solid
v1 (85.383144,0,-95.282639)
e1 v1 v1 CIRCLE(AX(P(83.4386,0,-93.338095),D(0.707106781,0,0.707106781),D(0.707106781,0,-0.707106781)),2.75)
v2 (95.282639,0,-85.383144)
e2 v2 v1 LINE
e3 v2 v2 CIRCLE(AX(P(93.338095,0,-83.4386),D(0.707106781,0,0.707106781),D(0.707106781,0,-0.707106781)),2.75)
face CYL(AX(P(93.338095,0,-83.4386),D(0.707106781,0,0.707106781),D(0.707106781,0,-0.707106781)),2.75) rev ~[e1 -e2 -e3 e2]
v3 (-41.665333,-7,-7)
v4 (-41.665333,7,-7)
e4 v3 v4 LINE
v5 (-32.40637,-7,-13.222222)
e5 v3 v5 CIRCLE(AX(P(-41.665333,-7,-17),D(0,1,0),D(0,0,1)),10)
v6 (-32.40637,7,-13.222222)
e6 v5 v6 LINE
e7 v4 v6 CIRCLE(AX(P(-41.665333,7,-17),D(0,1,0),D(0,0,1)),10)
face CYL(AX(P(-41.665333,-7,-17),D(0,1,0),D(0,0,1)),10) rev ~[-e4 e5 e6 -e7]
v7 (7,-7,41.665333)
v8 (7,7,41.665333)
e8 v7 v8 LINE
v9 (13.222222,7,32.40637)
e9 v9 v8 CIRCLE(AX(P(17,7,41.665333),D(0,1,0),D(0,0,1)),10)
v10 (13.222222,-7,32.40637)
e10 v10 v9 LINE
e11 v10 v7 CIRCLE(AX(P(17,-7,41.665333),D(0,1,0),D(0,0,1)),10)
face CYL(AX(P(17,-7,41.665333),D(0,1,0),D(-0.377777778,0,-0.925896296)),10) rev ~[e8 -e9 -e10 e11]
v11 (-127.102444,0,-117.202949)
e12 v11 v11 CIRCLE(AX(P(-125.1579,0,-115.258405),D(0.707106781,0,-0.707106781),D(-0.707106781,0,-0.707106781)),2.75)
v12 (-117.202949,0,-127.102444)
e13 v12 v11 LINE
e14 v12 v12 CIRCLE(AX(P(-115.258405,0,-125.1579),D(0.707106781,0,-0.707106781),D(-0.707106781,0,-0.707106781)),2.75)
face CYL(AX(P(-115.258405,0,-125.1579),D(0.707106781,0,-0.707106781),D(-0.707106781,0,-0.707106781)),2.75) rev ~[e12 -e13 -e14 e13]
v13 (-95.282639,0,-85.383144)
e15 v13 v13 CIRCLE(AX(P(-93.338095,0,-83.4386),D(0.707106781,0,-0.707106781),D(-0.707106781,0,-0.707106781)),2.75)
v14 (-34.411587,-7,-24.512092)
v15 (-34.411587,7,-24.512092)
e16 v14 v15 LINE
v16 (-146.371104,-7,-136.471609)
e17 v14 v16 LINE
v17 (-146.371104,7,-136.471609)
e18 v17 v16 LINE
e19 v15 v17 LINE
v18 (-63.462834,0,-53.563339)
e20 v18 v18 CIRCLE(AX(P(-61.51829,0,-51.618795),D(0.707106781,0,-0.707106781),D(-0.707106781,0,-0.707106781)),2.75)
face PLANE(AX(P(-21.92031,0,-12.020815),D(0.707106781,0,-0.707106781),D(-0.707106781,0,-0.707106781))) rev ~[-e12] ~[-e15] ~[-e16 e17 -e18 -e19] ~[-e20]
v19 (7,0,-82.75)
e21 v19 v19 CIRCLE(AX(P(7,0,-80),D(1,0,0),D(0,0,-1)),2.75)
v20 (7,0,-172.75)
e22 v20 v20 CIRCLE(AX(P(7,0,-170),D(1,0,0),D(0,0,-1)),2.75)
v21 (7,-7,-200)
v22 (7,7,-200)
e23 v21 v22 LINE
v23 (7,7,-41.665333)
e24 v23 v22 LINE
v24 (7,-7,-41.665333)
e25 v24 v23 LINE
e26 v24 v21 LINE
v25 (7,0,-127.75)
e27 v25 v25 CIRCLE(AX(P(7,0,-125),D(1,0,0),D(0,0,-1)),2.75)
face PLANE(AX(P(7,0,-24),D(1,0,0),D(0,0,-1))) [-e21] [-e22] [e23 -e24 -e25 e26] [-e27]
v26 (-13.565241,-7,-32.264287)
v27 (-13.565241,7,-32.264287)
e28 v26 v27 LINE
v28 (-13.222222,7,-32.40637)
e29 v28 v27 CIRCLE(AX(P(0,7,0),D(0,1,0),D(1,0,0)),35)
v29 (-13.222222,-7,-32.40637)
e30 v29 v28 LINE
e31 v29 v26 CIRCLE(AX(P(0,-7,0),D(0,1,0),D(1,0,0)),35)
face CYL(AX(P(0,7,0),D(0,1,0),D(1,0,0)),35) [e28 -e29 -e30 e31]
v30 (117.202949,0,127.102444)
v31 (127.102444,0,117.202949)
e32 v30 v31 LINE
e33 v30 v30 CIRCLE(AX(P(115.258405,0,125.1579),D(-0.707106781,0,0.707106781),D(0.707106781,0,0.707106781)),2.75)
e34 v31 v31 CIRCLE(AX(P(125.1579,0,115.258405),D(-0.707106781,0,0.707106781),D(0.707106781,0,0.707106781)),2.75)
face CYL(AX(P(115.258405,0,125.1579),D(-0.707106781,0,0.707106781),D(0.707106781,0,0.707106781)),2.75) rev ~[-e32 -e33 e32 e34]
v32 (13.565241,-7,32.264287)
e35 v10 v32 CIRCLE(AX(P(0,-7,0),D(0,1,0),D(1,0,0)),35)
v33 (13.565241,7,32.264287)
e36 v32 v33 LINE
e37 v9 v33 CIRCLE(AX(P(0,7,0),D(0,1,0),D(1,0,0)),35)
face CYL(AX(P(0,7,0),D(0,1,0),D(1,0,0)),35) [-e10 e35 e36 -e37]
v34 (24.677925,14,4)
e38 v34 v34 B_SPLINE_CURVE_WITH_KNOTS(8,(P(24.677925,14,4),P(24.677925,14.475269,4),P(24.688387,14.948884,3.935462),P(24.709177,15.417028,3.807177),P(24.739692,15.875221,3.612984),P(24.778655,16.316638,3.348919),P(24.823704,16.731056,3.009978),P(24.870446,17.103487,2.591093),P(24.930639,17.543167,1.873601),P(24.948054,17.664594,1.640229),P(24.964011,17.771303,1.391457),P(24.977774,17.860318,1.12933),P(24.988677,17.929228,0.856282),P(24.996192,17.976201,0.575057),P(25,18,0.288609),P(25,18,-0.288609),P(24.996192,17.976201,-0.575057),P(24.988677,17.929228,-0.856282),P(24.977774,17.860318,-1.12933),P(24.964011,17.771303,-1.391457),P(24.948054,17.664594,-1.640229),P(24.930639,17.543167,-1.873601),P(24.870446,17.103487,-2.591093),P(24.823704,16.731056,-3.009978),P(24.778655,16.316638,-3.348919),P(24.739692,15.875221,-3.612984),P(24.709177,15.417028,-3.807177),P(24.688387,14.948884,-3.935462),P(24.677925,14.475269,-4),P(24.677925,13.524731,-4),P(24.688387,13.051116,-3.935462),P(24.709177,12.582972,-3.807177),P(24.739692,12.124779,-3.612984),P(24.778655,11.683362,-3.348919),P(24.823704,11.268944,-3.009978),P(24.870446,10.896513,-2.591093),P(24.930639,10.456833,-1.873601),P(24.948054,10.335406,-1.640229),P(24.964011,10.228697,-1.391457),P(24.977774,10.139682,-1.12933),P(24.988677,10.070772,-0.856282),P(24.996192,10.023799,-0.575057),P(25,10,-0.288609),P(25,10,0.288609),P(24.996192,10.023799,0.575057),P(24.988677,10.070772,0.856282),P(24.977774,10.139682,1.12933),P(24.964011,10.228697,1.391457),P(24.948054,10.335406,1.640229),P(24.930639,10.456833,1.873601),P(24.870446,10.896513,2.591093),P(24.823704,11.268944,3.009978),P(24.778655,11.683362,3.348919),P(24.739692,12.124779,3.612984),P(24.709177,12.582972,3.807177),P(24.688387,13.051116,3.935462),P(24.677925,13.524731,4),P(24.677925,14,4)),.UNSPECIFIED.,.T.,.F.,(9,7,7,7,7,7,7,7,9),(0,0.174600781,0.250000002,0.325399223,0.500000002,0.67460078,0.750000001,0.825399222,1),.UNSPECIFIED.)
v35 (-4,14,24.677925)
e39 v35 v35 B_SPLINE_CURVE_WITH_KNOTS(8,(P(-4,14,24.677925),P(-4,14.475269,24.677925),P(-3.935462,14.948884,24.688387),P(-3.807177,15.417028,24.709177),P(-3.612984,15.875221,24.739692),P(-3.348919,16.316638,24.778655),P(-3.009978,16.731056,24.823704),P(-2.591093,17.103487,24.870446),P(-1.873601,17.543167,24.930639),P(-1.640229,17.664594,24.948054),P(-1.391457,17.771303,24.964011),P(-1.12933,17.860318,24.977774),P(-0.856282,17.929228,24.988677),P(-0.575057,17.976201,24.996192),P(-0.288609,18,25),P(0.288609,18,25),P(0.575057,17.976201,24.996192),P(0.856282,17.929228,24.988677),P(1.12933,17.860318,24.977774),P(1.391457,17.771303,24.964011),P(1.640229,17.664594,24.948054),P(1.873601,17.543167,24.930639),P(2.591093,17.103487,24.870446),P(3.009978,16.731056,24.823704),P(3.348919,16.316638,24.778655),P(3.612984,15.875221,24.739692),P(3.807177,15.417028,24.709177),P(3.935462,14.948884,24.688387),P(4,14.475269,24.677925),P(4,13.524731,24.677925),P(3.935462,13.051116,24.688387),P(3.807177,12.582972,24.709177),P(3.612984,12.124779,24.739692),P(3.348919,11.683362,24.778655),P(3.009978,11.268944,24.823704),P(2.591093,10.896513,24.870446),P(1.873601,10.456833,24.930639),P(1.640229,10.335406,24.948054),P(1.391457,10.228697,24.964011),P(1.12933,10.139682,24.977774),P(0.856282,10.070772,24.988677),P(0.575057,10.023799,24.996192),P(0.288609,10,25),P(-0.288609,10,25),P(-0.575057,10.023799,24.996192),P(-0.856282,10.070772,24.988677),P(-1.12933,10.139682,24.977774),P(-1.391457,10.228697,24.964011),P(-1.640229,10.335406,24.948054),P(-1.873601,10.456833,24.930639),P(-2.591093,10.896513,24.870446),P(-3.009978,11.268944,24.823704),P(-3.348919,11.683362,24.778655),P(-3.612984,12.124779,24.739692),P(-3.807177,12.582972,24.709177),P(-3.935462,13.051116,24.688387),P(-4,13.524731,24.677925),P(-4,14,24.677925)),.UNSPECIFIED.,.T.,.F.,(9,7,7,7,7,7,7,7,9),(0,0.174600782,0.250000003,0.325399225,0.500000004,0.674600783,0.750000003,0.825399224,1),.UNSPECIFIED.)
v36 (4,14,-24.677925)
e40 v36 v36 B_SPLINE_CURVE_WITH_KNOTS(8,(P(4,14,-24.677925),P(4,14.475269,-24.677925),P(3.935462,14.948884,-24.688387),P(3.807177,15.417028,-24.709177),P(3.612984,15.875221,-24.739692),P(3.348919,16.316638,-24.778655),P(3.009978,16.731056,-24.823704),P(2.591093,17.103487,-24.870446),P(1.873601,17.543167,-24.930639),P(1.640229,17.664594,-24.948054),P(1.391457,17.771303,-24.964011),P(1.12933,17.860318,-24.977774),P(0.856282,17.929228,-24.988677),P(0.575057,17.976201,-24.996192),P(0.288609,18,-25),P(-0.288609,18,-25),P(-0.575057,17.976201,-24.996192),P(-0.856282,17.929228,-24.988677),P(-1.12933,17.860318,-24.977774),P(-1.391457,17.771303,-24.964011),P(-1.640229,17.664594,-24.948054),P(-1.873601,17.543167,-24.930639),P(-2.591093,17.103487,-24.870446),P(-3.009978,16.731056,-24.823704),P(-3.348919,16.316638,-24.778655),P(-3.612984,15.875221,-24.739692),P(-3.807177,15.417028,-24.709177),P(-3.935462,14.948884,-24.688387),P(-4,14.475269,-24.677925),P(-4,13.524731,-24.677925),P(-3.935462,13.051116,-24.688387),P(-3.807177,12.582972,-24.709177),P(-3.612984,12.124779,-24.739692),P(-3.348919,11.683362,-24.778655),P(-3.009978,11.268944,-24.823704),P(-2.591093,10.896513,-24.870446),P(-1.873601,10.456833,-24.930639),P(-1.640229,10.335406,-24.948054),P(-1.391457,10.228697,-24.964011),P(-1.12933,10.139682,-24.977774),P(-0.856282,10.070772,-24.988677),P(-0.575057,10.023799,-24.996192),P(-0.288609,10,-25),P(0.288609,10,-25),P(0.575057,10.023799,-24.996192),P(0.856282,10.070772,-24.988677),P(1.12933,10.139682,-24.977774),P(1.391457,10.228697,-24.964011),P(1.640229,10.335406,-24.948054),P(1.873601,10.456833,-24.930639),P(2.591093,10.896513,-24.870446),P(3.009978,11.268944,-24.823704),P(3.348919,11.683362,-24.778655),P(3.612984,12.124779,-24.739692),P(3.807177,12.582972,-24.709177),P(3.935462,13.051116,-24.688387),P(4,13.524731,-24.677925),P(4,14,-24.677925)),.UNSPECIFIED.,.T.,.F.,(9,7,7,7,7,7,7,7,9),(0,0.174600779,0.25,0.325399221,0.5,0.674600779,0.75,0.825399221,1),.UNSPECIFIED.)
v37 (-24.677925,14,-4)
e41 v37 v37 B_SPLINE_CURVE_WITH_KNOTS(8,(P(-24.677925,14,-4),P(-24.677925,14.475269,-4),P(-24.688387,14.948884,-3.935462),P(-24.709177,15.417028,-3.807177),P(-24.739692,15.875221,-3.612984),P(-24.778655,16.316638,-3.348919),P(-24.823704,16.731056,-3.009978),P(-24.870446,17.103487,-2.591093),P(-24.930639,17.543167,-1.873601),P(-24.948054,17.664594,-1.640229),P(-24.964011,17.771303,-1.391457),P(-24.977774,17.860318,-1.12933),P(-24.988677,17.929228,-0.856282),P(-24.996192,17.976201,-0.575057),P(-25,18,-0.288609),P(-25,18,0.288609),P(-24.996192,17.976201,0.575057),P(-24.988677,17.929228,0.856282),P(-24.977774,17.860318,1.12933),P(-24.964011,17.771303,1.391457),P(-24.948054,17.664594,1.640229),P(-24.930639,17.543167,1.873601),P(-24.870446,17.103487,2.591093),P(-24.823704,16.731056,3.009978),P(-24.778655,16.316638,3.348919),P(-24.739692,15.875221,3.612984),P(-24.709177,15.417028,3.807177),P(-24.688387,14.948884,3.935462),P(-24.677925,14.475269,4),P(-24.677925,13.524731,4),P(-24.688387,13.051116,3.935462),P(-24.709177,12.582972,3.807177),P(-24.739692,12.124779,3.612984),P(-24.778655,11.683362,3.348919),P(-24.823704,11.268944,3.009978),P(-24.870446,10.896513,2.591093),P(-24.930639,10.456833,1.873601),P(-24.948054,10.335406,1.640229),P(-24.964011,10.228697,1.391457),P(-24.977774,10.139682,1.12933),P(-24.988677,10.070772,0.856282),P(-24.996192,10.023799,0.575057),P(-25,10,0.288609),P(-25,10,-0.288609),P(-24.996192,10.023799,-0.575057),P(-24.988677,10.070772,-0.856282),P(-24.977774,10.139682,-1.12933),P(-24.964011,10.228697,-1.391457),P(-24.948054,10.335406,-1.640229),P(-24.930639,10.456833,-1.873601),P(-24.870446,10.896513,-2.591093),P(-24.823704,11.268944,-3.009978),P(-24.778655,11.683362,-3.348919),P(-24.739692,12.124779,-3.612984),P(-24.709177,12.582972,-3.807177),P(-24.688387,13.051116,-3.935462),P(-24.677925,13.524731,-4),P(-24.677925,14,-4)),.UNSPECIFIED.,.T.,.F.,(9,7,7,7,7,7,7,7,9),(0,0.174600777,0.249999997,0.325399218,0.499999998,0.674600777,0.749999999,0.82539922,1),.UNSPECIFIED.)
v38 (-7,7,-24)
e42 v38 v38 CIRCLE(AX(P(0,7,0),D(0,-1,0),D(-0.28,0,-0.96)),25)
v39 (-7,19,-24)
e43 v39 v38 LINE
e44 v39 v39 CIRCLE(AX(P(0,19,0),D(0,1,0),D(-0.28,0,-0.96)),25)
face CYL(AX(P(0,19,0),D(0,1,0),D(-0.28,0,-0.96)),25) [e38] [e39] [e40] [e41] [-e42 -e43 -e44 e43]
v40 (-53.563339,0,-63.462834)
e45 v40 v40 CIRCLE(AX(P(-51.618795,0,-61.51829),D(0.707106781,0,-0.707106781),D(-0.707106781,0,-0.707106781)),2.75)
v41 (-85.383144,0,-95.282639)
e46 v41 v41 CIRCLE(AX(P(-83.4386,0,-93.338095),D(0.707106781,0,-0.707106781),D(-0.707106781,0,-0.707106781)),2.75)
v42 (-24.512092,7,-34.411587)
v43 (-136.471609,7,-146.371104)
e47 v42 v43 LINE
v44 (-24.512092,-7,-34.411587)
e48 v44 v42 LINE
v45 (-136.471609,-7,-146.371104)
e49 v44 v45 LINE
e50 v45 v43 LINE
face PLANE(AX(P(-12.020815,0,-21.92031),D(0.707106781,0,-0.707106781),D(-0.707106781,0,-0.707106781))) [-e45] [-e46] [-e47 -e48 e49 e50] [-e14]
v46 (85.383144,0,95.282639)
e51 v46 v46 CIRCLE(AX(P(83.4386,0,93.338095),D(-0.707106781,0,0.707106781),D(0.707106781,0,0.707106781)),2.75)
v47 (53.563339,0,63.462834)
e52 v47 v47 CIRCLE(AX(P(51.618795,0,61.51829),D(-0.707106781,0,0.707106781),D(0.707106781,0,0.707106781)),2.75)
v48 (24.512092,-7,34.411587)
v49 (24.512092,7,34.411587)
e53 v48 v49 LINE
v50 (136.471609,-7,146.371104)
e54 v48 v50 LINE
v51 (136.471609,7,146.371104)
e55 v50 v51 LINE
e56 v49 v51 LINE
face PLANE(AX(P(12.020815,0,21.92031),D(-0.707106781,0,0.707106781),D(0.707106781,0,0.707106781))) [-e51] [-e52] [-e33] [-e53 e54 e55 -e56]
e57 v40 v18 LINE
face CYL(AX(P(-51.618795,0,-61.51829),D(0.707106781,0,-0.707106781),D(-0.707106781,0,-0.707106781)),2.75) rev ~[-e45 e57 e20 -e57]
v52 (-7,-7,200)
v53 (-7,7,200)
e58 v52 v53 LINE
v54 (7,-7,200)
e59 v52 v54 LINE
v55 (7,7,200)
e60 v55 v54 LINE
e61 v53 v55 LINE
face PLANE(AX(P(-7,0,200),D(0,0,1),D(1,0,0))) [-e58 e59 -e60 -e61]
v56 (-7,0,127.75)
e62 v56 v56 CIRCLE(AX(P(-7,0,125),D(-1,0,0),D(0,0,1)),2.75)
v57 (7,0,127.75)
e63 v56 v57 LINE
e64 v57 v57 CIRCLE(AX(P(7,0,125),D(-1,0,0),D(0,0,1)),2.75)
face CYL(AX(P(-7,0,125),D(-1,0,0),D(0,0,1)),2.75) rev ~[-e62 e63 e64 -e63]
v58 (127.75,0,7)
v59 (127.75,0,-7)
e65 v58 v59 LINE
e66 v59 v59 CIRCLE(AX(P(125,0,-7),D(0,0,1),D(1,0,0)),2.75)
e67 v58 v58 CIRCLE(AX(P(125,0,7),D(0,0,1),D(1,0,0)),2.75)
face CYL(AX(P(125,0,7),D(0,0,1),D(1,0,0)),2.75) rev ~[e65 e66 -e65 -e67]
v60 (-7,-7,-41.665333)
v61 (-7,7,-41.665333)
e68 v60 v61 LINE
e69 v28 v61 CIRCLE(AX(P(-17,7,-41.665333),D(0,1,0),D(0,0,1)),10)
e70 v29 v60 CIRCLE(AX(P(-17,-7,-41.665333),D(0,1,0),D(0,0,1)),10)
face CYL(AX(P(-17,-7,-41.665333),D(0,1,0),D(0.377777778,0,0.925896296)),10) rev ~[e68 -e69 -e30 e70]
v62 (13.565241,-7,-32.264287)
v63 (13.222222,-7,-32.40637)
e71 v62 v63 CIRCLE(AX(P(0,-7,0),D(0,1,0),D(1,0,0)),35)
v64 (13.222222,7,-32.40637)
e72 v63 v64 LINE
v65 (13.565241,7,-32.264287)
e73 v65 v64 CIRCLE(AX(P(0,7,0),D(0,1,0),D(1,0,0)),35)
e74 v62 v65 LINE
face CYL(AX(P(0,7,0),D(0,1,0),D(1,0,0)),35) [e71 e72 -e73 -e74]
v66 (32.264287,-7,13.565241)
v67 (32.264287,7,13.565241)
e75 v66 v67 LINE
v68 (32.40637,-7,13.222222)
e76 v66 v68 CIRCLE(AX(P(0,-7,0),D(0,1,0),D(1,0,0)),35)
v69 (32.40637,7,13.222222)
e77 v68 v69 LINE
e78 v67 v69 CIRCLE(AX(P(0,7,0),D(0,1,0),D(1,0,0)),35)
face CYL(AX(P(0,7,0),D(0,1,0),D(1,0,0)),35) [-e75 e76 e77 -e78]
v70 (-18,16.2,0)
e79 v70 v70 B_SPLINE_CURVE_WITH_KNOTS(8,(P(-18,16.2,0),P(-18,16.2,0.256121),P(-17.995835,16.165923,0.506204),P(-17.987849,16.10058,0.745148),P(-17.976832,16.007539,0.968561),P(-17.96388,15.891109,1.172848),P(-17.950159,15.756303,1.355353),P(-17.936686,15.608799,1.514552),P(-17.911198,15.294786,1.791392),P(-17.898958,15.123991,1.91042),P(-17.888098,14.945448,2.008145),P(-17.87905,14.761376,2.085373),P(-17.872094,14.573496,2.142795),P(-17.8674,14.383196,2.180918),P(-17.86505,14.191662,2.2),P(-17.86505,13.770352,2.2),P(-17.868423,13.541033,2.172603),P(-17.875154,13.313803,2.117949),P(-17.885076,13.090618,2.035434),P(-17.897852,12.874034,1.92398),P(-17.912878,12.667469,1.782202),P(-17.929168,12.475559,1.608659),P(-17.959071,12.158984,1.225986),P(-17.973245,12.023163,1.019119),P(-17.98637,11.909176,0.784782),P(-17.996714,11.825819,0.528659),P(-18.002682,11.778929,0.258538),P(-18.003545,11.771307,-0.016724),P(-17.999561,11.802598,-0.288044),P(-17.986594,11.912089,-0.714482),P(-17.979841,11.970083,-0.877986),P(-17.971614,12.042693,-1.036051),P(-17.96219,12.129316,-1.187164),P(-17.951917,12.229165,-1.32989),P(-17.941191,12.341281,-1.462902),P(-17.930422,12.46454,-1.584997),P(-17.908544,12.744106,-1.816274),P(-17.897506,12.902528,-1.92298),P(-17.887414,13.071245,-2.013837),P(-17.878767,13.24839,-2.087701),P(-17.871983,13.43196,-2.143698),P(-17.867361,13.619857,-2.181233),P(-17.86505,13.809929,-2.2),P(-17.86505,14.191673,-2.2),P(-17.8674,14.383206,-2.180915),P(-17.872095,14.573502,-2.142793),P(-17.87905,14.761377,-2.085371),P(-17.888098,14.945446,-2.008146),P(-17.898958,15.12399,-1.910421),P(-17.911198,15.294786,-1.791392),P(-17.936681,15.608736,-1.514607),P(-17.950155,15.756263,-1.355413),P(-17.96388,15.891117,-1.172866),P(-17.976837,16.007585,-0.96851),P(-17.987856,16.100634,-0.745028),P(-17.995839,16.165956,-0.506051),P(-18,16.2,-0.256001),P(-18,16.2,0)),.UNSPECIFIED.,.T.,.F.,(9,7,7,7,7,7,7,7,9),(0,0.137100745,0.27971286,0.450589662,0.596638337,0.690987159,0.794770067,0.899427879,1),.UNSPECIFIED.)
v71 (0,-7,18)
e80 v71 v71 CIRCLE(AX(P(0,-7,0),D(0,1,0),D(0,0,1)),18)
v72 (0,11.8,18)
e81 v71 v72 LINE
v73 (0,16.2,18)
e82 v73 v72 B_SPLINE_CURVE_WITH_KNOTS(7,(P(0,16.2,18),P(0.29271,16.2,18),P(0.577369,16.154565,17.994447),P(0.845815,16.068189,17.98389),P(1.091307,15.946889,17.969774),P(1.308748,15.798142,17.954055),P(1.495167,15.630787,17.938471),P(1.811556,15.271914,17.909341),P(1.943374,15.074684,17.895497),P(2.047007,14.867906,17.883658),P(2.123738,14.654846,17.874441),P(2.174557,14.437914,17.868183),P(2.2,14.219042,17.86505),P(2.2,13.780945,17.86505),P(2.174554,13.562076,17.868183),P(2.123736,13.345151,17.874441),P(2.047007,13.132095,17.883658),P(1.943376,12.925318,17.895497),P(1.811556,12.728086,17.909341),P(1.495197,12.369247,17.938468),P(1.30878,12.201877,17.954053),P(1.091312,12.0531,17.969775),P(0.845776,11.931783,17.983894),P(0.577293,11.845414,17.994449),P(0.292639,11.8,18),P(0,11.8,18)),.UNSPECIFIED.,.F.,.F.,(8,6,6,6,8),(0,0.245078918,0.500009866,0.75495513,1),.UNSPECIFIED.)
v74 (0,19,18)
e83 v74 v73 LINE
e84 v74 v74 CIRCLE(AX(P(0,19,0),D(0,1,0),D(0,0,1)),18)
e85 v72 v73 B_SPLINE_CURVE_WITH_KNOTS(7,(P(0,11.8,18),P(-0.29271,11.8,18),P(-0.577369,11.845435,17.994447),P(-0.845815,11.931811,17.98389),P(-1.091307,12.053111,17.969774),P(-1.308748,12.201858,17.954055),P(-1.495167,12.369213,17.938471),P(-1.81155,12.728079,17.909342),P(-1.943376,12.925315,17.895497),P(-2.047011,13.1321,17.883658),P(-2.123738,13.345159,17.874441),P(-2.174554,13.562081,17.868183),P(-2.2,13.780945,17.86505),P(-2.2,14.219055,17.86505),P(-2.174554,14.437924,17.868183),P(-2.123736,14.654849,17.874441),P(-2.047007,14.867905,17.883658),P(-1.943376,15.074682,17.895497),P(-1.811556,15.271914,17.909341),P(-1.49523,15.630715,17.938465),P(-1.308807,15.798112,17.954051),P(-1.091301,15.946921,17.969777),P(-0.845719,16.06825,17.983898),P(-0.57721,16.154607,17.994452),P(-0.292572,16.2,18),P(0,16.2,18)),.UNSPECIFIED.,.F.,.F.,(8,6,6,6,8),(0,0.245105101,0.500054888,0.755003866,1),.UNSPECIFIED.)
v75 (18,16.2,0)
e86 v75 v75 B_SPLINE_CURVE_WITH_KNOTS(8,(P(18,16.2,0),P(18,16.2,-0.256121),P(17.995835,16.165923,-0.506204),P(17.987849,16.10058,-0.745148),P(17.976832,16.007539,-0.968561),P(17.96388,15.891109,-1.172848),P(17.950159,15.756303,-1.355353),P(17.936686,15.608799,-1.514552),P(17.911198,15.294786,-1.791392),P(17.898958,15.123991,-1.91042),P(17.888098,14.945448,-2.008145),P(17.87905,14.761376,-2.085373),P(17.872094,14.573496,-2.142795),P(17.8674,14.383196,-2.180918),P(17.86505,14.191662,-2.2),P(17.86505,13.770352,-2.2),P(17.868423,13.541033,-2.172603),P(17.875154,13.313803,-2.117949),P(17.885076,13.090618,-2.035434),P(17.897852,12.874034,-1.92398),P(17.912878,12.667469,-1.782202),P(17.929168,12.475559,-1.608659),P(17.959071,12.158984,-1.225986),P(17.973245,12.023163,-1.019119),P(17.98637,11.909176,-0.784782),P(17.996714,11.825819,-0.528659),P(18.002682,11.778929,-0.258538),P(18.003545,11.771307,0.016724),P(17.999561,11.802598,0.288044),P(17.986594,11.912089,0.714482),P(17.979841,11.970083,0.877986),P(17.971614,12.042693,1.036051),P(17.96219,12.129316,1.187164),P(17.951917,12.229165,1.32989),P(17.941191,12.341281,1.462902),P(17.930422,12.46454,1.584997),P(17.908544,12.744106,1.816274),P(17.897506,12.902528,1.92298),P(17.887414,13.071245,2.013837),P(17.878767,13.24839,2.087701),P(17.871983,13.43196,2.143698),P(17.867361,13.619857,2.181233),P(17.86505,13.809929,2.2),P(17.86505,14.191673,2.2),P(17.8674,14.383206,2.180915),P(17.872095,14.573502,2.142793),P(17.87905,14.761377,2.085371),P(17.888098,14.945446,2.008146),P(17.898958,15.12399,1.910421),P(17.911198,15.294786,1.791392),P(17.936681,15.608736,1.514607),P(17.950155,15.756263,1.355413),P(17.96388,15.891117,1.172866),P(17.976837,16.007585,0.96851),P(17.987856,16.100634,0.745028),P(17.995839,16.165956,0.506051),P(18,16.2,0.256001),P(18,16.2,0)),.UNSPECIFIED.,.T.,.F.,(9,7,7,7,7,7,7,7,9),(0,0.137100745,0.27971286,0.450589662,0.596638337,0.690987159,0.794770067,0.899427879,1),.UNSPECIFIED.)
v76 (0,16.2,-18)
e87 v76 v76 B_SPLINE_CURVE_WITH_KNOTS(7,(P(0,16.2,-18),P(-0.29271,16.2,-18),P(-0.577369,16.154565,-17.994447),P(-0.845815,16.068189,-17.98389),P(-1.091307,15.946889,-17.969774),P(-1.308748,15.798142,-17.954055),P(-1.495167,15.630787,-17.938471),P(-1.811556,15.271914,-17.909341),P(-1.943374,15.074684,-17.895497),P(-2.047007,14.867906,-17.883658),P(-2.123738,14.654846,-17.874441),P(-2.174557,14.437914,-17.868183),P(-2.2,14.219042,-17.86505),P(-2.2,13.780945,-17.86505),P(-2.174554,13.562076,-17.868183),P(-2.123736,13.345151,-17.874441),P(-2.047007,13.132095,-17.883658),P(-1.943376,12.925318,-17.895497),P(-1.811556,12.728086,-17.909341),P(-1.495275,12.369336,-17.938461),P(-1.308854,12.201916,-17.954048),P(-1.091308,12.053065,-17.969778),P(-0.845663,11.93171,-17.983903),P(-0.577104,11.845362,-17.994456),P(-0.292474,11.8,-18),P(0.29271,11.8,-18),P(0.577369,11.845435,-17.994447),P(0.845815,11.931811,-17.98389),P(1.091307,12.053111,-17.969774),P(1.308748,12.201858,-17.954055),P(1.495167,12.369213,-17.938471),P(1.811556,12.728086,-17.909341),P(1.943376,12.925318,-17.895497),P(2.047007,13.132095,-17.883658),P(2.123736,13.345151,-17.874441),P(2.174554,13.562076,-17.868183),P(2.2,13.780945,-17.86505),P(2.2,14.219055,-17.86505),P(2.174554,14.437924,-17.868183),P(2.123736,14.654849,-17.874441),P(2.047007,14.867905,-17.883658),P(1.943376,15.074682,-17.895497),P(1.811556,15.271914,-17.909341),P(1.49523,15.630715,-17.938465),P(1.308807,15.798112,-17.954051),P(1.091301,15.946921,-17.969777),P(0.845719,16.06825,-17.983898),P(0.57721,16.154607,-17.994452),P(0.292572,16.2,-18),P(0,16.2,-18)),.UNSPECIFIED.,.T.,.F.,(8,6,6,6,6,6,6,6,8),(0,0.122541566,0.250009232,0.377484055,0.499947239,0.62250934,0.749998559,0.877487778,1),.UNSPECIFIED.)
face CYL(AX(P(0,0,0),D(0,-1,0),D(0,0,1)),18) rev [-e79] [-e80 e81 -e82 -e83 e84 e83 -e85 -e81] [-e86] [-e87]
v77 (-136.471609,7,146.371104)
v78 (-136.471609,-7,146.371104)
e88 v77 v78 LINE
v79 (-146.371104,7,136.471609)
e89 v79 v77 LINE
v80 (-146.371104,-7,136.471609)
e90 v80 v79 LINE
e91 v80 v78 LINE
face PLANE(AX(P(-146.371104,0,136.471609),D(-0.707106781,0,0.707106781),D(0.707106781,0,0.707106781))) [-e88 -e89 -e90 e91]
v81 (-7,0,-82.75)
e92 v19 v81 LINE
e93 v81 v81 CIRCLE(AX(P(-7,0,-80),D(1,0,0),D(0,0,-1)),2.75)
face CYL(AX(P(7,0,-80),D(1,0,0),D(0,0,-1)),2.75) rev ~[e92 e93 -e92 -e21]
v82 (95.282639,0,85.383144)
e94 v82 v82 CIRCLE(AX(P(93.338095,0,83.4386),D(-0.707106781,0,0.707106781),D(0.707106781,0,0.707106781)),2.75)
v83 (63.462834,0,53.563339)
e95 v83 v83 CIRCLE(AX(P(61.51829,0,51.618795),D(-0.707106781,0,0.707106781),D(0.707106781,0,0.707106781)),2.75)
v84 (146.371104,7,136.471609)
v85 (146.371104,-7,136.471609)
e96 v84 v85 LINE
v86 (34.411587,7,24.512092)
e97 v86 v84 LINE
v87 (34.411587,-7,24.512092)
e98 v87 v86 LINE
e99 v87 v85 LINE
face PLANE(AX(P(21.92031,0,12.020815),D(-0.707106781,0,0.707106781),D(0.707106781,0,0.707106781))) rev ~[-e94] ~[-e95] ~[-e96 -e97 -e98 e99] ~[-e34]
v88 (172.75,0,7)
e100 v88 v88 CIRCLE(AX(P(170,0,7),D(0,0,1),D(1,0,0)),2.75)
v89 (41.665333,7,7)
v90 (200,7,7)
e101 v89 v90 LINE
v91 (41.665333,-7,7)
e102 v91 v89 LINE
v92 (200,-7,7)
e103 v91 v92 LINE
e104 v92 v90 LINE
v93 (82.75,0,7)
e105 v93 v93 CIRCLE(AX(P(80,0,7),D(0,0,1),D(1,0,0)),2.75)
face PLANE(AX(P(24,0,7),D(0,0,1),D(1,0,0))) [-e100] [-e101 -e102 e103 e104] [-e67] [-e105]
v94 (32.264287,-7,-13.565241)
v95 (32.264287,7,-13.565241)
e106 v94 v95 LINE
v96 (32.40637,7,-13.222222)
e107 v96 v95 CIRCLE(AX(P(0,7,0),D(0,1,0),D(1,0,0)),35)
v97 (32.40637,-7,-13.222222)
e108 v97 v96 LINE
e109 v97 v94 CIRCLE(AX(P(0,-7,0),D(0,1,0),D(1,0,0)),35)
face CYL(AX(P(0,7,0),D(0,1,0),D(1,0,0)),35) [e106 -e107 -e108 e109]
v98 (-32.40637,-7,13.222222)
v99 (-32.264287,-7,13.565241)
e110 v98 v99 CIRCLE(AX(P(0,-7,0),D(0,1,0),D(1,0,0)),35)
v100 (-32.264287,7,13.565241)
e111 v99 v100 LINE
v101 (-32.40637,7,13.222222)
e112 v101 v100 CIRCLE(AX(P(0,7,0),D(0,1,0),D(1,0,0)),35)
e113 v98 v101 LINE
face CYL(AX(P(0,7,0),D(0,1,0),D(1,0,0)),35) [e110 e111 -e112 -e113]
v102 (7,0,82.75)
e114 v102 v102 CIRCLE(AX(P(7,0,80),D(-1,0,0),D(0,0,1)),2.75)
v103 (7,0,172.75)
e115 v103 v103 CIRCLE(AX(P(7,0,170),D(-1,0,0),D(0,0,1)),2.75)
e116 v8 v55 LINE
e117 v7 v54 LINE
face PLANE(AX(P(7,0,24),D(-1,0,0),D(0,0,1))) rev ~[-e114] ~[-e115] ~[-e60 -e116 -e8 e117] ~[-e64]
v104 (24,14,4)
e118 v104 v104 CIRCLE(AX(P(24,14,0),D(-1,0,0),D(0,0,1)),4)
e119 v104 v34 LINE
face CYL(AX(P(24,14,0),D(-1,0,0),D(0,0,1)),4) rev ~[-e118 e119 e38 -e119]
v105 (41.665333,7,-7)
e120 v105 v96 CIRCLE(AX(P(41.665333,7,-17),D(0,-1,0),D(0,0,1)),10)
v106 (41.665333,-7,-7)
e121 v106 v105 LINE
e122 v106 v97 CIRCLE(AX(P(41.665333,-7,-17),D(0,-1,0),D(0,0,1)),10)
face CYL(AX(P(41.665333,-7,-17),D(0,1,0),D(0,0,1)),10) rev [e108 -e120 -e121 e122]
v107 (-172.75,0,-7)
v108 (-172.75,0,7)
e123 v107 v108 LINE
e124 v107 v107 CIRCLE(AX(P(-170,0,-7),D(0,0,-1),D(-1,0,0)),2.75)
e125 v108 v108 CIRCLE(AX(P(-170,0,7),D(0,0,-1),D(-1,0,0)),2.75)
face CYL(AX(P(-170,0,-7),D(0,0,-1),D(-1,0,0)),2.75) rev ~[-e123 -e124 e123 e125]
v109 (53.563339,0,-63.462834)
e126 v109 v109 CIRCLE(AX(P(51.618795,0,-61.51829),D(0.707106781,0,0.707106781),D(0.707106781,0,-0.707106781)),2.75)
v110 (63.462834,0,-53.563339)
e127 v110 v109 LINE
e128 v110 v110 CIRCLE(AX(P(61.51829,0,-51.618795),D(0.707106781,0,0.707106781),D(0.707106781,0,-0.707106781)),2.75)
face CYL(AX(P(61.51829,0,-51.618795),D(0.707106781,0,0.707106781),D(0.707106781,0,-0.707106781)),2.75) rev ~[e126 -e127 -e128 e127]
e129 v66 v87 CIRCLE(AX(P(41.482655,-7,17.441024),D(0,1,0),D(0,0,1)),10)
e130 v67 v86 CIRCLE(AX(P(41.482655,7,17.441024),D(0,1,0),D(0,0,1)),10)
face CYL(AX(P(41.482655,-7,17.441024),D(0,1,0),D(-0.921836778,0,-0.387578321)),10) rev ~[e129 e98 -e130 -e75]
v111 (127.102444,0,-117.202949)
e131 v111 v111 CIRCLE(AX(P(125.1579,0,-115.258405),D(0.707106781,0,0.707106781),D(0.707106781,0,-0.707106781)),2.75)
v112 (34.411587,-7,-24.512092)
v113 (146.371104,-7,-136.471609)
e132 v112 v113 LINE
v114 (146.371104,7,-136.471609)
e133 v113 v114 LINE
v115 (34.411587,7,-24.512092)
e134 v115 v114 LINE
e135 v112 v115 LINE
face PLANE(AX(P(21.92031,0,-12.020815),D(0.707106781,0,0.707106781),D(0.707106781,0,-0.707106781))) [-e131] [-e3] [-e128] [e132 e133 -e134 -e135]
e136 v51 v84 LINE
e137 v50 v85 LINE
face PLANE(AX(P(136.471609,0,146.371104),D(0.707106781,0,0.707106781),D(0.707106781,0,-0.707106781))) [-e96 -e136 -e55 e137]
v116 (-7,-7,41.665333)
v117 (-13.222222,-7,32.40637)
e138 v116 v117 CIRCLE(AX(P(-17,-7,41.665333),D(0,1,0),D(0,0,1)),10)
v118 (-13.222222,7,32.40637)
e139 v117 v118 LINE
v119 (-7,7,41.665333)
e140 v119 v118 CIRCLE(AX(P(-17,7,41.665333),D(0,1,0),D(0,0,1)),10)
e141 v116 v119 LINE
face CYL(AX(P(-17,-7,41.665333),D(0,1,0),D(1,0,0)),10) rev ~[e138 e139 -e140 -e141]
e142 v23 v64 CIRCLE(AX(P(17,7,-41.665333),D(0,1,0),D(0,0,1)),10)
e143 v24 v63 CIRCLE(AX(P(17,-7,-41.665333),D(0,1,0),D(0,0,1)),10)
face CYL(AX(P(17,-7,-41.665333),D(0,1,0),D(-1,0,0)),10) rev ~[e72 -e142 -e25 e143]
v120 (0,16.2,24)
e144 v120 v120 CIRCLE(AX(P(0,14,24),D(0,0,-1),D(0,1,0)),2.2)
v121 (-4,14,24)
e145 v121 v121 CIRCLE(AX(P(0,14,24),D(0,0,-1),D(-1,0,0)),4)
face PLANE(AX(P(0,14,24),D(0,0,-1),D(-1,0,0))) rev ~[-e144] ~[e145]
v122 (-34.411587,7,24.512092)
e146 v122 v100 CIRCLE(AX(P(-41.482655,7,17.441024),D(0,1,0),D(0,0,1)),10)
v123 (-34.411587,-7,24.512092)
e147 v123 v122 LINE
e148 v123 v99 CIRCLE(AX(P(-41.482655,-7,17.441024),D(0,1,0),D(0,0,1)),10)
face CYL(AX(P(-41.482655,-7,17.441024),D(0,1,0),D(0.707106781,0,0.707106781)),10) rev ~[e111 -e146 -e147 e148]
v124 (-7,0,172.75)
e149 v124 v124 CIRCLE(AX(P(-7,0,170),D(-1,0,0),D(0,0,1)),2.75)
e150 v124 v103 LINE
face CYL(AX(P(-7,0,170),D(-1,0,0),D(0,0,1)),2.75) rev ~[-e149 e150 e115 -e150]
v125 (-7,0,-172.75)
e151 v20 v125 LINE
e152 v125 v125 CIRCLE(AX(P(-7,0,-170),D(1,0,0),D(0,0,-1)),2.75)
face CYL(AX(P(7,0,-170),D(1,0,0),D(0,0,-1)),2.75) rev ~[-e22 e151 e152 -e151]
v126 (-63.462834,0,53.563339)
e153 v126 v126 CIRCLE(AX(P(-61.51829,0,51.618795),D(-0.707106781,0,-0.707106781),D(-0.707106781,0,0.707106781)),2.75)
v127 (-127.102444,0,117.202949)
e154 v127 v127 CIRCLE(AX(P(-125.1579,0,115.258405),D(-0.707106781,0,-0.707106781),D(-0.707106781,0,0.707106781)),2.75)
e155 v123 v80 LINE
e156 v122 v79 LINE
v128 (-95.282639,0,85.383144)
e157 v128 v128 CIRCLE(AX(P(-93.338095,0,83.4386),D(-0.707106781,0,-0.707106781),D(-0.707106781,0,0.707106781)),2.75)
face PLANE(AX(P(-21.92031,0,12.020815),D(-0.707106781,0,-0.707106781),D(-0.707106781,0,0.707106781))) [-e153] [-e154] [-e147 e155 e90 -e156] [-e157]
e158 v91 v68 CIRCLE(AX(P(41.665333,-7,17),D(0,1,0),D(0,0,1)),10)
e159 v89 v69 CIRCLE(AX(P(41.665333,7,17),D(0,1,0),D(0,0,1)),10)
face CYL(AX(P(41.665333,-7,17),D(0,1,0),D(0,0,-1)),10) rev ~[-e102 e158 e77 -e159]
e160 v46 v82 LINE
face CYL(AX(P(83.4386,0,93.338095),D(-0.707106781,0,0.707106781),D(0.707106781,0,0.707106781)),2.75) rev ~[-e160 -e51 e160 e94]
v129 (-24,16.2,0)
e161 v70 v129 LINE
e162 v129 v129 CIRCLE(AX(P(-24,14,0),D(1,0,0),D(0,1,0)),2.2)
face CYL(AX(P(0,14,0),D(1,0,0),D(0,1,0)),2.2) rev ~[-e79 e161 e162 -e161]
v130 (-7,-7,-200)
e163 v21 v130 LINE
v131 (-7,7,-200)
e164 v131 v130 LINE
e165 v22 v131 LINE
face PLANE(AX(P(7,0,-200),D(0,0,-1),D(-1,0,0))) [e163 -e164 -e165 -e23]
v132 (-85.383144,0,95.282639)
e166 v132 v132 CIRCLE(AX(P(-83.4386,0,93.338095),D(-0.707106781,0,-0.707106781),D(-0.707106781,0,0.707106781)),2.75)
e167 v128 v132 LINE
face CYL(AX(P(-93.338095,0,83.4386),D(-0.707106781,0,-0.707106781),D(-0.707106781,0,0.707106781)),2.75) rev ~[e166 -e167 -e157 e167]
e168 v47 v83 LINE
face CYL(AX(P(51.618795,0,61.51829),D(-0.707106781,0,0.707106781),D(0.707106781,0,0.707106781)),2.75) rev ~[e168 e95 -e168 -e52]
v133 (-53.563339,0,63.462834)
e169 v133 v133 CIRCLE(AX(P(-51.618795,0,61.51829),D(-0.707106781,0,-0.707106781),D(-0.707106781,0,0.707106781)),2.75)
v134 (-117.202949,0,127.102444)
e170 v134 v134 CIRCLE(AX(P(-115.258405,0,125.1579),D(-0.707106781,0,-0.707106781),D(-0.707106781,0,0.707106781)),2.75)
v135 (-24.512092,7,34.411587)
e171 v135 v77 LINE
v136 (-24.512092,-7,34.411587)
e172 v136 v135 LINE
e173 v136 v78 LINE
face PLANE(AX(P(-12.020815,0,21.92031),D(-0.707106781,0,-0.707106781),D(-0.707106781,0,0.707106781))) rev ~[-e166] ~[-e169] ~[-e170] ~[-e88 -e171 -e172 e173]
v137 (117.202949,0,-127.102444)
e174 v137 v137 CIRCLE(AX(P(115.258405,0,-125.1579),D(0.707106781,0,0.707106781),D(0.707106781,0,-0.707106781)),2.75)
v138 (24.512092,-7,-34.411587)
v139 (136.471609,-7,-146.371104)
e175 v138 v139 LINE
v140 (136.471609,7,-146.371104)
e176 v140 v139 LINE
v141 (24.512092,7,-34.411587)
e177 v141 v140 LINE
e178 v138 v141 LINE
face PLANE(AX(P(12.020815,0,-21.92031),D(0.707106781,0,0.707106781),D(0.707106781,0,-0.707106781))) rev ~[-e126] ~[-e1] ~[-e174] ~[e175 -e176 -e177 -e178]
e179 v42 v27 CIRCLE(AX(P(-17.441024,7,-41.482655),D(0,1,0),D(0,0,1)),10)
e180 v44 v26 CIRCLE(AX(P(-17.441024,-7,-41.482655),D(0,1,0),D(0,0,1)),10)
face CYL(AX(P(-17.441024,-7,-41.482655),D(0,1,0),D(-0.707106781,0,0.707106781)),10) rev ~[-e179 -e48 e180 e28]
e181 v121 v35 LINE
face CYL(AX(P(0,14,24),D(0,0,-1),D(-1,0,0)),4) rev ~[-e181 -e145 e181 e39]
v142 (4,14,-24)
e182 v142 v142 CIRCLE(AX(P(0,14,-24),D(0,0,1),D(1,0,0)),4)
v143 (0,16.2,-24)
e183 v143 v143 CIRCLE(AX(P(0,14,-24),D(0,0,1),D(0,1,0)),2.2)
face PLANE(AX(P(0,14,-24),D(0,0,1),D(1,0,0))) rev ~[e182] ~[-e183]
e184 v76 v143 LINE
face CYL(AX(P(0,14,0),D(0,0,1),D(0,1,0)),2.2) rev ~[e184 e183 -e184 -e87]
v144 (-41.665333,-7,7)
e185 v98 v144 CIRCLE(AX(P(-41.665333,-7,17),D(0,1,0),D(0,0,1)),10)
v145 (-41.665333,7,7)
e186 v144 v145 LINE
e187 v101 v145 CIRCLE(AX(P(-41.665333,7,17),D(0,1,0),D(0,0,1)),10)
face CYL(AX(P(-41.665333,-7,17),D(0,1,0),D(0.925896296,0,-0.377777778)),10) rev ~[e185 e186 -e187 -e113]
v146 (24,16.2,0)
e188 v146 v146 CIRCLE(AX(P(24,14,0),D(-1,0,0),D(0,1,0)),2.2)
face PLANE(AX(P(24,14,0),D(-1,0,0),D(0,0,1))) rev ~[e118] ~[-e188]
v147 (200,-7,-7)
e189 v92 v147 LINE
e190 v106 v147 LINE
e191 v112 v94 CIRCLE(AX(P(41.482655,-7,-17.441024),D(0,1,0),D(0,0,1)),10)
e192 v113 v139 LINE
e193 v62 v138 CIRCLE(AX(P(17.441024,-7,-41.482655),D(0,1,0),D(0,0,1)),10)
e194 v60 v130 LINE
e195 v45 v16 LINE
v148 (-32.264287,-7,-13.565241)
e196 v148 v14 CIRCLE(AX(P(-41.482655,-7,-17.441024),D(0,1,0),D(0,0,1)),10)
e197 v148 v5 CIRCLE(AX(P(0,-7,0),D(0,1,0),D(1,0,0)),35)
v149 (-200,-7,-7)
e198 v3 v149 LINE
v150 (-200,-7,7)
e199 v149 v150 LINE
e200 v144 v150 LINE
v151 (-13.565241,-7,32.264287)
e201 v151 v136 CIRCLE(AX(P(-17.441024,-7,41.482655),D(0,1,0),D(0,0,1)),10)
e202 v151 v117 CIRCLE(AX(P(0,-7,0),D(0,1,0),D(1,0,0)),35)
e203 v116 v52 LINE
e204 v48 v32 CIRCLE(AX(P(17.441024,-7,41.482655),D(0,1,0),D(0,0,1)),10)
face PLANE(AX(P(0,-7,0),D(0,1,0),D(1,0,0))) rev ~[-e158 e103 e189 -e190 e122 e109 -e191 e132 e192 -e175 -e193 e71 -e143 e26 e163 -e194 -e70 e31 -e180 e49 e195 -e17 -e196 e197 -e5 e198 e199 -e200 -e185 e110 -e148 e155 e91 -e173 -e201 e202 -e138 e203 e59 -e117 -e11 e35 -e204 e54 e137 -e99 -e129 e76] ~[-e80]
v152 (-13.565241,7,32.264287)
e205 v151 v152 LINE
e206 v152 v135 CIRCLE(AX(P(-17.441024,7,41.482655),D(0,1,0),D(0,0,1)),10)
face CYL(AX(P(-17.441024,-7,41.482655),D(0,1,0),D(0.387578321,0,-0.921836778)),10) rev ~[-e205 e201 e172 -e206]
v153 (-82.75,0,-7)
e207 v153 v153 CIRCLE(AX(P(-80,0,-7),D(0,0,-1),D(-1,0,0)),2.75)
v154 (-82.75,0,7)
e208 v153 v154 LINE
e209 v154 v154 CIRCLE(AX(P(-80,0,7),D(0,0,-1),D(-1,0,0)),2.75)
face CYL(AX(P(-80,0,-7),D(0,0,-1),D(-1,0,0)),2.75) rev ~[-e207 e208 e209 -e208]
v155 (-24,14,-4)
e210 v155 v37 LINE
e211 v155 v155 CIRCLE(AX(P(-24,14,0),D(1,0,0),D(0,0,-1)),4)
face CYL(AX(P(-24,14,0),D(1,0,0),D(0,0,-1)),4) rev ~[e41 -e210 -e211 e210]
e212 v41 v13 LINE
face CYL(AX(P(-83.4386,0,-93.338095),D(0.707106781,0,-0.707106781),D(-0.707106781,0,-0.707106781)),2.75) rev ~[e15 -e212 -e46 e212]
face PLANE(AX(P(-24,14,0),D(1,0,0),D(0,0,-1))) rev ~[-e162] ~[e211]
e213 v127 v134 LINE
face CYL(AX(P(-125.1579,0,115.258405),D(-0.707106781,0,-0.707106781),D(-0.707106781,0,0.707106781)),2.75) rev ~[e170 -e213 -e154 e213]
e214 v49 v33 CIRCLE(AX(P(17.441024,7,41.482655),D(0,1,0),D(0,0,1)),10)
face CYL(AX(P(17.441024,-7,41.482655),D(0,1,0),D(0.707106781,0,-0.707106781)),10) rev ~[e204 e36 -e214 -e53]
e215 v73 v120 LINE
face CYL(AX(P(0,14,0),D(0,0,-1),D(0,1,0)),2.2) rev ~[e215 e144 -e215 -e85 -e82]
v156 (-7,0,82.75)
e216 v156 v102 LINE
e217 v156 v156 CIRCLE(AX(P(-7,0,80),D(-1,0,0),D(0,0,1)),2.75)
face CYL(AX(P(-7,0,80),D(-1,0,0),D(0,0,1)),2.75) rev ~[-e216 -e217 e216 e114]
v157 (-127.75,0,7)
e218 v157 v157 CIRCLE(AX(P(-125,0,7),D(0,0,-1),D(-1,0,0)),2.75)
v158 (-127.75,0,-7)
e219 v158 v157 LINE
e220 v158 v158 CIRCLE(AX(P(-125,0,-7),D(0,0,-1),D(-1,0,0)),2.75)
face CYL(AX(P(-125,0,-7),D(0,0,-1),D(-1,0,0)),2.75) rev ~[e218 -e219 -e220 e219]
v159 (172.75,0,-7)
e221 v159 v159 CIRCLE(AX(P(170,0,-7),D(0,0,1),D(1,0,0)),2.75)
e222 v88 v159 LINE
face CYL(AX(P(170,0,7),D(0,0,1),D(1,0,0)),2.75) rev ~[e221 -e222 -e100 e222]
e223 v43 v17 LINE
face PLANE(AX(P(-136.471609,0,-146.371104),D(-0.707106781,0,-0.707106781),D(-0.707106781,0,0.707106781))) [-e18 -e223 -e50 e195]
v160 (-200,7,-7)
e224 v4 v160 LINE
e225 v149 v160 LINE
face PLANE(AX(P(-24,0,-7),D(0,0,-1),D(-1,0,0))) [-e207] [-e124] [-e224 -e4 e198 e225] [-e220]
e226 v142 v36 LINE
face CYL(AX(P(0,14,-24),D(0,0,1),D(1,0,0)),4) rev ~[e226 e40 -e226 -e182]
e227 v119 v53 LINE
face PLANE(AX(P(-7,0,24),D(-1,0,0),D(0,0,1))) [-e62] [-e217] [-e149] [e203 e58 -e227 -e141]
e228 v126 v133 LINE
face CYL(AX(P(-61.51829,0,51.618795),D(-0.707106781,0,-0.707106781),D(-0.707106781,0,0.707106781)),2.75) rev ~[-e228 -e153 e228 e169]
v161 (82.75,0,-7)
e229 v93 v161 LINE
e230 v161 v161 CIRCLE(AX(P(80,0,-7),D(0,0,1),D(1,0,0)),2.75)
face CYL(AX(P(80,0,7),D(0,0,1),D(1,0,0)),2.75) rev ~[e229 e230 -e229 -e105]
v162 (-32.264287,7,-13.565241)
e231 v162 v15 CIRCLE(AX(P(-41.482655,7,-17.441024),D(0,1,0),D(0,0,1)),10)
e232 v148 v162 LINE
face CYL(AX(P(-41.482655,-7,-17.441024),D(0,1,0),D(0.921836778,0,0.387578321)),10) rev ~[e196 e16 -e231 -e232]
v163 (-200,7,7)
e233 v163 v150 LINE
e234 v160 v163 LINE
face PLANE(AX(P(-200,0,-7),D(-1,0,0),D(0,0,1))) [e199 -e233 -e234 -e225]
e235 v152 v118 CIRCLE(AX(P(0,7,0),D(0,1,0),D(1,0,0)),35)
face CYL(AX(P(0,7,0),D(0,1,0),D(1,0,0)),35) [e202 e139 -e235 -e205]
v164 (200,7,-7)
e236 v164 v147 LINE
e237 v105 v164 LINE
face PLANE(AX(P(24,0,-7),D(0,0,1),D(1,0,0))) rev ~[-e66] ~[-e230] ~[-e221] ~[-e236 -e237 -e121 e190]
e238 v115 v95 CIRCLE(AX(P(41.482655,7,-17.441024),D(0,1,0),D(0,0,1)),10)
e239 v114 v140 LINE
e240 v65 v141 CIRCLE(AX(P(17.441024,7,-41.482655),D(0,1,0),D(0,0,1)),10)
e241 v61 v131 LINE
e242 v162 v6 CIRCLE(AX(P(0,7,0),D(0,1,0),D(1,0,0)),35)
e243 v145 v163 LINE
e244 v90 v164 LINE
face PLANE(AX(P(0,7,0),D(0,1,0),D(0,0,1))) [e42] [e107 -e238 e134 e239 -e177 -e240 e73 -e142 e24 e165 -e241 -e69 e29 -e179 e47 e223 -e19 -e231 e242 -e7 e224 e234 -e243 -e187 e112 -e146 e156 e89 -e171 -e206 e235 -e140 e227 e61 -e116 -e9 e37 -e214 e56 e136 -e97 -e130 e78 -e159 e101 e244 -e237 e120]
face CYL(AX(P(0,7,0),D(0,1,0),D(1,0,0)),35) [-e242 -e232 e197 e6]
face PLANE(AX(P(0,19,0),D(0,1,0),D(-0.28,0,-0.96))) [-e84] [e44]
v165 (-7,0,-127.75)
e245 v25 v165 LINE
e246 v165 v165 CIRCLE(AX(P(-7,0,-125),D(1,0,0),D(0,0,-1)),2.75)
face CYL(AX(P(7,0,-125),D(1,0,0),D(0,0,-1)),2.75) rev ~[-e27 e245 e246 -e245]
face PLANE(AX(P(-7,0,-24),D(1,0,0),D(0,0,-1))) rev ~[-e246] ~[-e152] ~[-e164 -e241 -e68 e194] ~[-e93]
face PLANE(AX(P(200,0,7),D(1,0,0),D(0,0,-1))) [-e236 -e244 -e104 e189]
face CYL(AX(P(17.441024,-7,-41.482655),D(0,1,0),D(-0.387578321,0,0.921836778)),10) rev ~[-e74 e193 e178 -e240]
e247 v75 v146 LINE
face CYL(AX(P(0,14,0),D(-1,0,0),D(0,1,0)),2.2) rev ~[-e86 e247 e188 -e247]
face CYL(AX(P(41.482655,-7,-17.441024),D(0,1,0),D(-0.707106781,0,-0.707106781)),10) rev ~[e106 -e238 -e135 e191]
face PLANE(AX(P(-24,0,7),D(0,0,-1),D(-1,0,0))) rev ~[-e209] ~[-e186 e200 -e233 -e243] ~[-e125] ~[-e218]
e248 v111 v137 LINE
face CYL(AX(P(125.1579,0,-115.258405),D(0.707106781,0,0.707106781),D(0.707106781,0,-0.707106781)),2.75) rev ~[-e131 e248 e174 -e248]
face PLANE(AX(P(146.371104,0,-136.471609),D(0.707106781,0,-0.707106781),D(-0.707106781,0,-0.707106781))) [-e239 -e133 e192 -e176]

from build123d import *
from build123d.topology import SkipClean

# Parameters (mm, degrees)
SKETCH_3_R               = 25
SKETCH_3_R_2             = 18
EXTRUDE_4_DEPTH          = 7
SKETCH_4_W               = 176
SKETCH_4_H               = 14
EXTRUDE_5_DEPTH          = 7
SKETCH_5_R               = 2.75
CUT_EXTRUDE_1_DEPTH      = 14
PATTERN_CIRCULAR_1_COUNT = 8
EXTRUDE_START            = 12
SKETCH_6_R               = 25
SKETCH_6_R_2             = 18
EXTRUDE_6_DEPTH          = 12
SKETCH_7_R               = 2.2
CUT_EXTRUDE_2_DEPTH      = 43
CUT_EXTRUDE_START        = -24
SKETCH_8_R               = 4
CUT_EXTRUDE_4_DEPTH      = 43
PATTERN_CIRCULAR_2_COUNT = 4
SKETCH_10_R              = 35
SKETCH_10_R_2            = 25
EXTRUDE_7_DEPTH          = 14
FILLET_2_R               = 10


with BuildPart() as part:
    # 草图3 → 凸台-拉伸4 (new, symmetric)
    with BuildSketch(Plane(origin=(0, 0, 0), x_dir=(1, 0, 0), z_dir=(0, 1, 0))):
        with Locations(Location((0, 0, 0), (0, 0, 270))):
            Circle(SKETCH_3_R)
        with Locations(Location((0, 0, 0), (0, 0, 270))):
            Circle(SKETCH_3_R_2, mode=Mode.SUBTRACT)
    extrude(amount=EXTRUDE_4_DEPTH, both=True)

    # 草图4 → 凸台-拉伸5 (add, symmetric)
    with BuildSketch(Plane(origin=(0, 0, 0), x_dir=(1, 0, 0), z_dir=(0, 1, 0))):
        with Locations((112, 0)):
            Rectangle(SKETCH_4_W, SKETCH_4_H)
    extrude_5 = extrude(amount=EXTRUDE_5_DEPTH, both=True)

    # 草图5 → 切除-拉伸1 (cut)
    with BuildSketch(Plane.XY.offset(7)):
        with Locations((80, 0)):
            Circle(SKETCH_5_R)
        with Locations((125, 0)):
            Circle(SKETCH_5_R)
        with Locations((170, 0)):
            Circle(SKETCH_5_R)
    cut_extrude_1 = extrude(amount=-CUT_EXTRUDE_1_DEPTH, mode=Mode.SUBTRACT)

    # 阵列(圆周)1: 凸台-拉伸5, 切除-拉伸1 ×8 about axis
    pattern_circular_1_axis = Axis((0, 0, 0), (0, 1, 0))
    add([extrude_5.rotate(pattern_circular_1_axis, i * 360 / PATTERN_CIRCULAR_1_COUNT) for i in range(1, PATTERN_CIRCULAR_1_COUNT)])
    add([cut_extrude_1.rotate(pattern_circular_1_axis, i * 360 / PATTERN_CIRCULAR_1_COUNT) for i in range(1, PATTERN_CIRCULAR_1_COUNT)], mode=Mode.SUBTRACT)

    # 草图6 → 凸台-拉伸6 (add)
    with SkipClean():  # the faces are left unmerged after this step: merging them gives an invalid solid
        with BuildSketch(Plane(origin=(0, 7, 0), x_dir=(1, 0, 0), z_dir=(0, 1, 0)).offset(EXTRUDE_START)):
            with Locations(Location((0, 0, 0), (0, 0, 106.260204708))):
                Circle(SKETCH_6_R)
            with Locations(Location((0, 0, 0), (0, 0, 270))):
                Circle(SKETCH_6_R_2, mode=Mode.SUBTRACT)
        extrude(amount=-EXTRUDE_6_DEPTH)

    # 草图7 → 切除-拉伸2 (cut)
    with SkipClean():  # the faces are left unmerged after this step: merging them gives an invalid solid
        with BuildSketch(Plane.XY):
            with Locations(Location((0, 14, 0), (0, 0, 90))):
                Circle(SKETCH_7_R)
        cut_extrude_2 = extrude(amount=-CUT_EXTRUDE_2_DEPTH, mode=Mode.SUBTRACT)

    # 草图8 → 切除-拉伸4 (cut)
    with SkipClean():  # the faces are left unmerged after this step: merging them gives an invalid solid
        with BuildSketch(Plane.XY.offset(CUT_EXTRUDE_START)):
            with Locations((0, 14)):
                Circle(SKETCH_8_R)
        cut_extrude_4 = extrude(amount=-CUT_EXTRUDE_4_DEPTH, mode=Mode.SUBTRACT)

    # 阵列(圆周)2: 切除-拉伸2, 切除-拉伸4 ×4 about axis
    with SkipClean():  # the faces are left unmerged after this step: merging them gives an invalid solid
        pattern_circular_2_axis = Axis((0, 0, 0), (0, 1, 0))
        add([cut_extrude_2.rotate(pattern_circular_2_axis, i * 360 / PATTERN_CIRCULAR_2_COUNT) for i in range(1, PATTERN_CIRCULAR_2_COUNT)], mode=Mode.SUBTRACT)
        add([cut_extrude_4.rotate(pattern_circular_2_axis, i * 360 / PATTERN_CIRCULAR_2_COUNT) for i in range(1, PATTERN_CIRCULAR_2_COUNT)], mode=Mode.SUBTRACT)

    # 草图10 → 凸台-拉伸7 (add)
    with BuildSketch(Plane(origin=(0, 7, 0), x_dir=(1, 0, 0), z_dir=(0, 1, 0))):
        Circle(SKETCH_10_R)
        with Locations(Location((0, 0, 0), (0, 0, 270))):
            Circle(SKETCH_10_R_2, mode=Mode.SUBTRACT)
    extrude(amount=-EXTRUDE_7_DEPTH)

    # 圆角2
    fillet_2_edges = [part.edges().sort_by_distance(p)[0] for p in [
        (19.298963838, 0, -29.198458774),
        (34.292856399, 0, 7),
        (34.292856399, 0, -7),
        (19.298963838, 0, 29.198458774),
        (29.198458774, 0, 19.298963838),
        (-7, 0, 34.292856399),
        (7, 0, 34.292856399),
        (-29.198458774, 0, 19.298963838),
        (-19.298963838, 0, 29.198458774),
        (-34.292856399, 0, -7),
        (-34.292856399, 0, 7),
        (-19.298963838, 0, -29.198458774),
        (-29.198458774, 0, -19.298963838),
        (7, 0, -34.292856399),
        (-7, 0, -34.292856399),
        (29.198458774, 0, -19.298963838),
    ]]
    fillet(fillet_2_edges, radius=FILLET_2_R)


solid = part.part
